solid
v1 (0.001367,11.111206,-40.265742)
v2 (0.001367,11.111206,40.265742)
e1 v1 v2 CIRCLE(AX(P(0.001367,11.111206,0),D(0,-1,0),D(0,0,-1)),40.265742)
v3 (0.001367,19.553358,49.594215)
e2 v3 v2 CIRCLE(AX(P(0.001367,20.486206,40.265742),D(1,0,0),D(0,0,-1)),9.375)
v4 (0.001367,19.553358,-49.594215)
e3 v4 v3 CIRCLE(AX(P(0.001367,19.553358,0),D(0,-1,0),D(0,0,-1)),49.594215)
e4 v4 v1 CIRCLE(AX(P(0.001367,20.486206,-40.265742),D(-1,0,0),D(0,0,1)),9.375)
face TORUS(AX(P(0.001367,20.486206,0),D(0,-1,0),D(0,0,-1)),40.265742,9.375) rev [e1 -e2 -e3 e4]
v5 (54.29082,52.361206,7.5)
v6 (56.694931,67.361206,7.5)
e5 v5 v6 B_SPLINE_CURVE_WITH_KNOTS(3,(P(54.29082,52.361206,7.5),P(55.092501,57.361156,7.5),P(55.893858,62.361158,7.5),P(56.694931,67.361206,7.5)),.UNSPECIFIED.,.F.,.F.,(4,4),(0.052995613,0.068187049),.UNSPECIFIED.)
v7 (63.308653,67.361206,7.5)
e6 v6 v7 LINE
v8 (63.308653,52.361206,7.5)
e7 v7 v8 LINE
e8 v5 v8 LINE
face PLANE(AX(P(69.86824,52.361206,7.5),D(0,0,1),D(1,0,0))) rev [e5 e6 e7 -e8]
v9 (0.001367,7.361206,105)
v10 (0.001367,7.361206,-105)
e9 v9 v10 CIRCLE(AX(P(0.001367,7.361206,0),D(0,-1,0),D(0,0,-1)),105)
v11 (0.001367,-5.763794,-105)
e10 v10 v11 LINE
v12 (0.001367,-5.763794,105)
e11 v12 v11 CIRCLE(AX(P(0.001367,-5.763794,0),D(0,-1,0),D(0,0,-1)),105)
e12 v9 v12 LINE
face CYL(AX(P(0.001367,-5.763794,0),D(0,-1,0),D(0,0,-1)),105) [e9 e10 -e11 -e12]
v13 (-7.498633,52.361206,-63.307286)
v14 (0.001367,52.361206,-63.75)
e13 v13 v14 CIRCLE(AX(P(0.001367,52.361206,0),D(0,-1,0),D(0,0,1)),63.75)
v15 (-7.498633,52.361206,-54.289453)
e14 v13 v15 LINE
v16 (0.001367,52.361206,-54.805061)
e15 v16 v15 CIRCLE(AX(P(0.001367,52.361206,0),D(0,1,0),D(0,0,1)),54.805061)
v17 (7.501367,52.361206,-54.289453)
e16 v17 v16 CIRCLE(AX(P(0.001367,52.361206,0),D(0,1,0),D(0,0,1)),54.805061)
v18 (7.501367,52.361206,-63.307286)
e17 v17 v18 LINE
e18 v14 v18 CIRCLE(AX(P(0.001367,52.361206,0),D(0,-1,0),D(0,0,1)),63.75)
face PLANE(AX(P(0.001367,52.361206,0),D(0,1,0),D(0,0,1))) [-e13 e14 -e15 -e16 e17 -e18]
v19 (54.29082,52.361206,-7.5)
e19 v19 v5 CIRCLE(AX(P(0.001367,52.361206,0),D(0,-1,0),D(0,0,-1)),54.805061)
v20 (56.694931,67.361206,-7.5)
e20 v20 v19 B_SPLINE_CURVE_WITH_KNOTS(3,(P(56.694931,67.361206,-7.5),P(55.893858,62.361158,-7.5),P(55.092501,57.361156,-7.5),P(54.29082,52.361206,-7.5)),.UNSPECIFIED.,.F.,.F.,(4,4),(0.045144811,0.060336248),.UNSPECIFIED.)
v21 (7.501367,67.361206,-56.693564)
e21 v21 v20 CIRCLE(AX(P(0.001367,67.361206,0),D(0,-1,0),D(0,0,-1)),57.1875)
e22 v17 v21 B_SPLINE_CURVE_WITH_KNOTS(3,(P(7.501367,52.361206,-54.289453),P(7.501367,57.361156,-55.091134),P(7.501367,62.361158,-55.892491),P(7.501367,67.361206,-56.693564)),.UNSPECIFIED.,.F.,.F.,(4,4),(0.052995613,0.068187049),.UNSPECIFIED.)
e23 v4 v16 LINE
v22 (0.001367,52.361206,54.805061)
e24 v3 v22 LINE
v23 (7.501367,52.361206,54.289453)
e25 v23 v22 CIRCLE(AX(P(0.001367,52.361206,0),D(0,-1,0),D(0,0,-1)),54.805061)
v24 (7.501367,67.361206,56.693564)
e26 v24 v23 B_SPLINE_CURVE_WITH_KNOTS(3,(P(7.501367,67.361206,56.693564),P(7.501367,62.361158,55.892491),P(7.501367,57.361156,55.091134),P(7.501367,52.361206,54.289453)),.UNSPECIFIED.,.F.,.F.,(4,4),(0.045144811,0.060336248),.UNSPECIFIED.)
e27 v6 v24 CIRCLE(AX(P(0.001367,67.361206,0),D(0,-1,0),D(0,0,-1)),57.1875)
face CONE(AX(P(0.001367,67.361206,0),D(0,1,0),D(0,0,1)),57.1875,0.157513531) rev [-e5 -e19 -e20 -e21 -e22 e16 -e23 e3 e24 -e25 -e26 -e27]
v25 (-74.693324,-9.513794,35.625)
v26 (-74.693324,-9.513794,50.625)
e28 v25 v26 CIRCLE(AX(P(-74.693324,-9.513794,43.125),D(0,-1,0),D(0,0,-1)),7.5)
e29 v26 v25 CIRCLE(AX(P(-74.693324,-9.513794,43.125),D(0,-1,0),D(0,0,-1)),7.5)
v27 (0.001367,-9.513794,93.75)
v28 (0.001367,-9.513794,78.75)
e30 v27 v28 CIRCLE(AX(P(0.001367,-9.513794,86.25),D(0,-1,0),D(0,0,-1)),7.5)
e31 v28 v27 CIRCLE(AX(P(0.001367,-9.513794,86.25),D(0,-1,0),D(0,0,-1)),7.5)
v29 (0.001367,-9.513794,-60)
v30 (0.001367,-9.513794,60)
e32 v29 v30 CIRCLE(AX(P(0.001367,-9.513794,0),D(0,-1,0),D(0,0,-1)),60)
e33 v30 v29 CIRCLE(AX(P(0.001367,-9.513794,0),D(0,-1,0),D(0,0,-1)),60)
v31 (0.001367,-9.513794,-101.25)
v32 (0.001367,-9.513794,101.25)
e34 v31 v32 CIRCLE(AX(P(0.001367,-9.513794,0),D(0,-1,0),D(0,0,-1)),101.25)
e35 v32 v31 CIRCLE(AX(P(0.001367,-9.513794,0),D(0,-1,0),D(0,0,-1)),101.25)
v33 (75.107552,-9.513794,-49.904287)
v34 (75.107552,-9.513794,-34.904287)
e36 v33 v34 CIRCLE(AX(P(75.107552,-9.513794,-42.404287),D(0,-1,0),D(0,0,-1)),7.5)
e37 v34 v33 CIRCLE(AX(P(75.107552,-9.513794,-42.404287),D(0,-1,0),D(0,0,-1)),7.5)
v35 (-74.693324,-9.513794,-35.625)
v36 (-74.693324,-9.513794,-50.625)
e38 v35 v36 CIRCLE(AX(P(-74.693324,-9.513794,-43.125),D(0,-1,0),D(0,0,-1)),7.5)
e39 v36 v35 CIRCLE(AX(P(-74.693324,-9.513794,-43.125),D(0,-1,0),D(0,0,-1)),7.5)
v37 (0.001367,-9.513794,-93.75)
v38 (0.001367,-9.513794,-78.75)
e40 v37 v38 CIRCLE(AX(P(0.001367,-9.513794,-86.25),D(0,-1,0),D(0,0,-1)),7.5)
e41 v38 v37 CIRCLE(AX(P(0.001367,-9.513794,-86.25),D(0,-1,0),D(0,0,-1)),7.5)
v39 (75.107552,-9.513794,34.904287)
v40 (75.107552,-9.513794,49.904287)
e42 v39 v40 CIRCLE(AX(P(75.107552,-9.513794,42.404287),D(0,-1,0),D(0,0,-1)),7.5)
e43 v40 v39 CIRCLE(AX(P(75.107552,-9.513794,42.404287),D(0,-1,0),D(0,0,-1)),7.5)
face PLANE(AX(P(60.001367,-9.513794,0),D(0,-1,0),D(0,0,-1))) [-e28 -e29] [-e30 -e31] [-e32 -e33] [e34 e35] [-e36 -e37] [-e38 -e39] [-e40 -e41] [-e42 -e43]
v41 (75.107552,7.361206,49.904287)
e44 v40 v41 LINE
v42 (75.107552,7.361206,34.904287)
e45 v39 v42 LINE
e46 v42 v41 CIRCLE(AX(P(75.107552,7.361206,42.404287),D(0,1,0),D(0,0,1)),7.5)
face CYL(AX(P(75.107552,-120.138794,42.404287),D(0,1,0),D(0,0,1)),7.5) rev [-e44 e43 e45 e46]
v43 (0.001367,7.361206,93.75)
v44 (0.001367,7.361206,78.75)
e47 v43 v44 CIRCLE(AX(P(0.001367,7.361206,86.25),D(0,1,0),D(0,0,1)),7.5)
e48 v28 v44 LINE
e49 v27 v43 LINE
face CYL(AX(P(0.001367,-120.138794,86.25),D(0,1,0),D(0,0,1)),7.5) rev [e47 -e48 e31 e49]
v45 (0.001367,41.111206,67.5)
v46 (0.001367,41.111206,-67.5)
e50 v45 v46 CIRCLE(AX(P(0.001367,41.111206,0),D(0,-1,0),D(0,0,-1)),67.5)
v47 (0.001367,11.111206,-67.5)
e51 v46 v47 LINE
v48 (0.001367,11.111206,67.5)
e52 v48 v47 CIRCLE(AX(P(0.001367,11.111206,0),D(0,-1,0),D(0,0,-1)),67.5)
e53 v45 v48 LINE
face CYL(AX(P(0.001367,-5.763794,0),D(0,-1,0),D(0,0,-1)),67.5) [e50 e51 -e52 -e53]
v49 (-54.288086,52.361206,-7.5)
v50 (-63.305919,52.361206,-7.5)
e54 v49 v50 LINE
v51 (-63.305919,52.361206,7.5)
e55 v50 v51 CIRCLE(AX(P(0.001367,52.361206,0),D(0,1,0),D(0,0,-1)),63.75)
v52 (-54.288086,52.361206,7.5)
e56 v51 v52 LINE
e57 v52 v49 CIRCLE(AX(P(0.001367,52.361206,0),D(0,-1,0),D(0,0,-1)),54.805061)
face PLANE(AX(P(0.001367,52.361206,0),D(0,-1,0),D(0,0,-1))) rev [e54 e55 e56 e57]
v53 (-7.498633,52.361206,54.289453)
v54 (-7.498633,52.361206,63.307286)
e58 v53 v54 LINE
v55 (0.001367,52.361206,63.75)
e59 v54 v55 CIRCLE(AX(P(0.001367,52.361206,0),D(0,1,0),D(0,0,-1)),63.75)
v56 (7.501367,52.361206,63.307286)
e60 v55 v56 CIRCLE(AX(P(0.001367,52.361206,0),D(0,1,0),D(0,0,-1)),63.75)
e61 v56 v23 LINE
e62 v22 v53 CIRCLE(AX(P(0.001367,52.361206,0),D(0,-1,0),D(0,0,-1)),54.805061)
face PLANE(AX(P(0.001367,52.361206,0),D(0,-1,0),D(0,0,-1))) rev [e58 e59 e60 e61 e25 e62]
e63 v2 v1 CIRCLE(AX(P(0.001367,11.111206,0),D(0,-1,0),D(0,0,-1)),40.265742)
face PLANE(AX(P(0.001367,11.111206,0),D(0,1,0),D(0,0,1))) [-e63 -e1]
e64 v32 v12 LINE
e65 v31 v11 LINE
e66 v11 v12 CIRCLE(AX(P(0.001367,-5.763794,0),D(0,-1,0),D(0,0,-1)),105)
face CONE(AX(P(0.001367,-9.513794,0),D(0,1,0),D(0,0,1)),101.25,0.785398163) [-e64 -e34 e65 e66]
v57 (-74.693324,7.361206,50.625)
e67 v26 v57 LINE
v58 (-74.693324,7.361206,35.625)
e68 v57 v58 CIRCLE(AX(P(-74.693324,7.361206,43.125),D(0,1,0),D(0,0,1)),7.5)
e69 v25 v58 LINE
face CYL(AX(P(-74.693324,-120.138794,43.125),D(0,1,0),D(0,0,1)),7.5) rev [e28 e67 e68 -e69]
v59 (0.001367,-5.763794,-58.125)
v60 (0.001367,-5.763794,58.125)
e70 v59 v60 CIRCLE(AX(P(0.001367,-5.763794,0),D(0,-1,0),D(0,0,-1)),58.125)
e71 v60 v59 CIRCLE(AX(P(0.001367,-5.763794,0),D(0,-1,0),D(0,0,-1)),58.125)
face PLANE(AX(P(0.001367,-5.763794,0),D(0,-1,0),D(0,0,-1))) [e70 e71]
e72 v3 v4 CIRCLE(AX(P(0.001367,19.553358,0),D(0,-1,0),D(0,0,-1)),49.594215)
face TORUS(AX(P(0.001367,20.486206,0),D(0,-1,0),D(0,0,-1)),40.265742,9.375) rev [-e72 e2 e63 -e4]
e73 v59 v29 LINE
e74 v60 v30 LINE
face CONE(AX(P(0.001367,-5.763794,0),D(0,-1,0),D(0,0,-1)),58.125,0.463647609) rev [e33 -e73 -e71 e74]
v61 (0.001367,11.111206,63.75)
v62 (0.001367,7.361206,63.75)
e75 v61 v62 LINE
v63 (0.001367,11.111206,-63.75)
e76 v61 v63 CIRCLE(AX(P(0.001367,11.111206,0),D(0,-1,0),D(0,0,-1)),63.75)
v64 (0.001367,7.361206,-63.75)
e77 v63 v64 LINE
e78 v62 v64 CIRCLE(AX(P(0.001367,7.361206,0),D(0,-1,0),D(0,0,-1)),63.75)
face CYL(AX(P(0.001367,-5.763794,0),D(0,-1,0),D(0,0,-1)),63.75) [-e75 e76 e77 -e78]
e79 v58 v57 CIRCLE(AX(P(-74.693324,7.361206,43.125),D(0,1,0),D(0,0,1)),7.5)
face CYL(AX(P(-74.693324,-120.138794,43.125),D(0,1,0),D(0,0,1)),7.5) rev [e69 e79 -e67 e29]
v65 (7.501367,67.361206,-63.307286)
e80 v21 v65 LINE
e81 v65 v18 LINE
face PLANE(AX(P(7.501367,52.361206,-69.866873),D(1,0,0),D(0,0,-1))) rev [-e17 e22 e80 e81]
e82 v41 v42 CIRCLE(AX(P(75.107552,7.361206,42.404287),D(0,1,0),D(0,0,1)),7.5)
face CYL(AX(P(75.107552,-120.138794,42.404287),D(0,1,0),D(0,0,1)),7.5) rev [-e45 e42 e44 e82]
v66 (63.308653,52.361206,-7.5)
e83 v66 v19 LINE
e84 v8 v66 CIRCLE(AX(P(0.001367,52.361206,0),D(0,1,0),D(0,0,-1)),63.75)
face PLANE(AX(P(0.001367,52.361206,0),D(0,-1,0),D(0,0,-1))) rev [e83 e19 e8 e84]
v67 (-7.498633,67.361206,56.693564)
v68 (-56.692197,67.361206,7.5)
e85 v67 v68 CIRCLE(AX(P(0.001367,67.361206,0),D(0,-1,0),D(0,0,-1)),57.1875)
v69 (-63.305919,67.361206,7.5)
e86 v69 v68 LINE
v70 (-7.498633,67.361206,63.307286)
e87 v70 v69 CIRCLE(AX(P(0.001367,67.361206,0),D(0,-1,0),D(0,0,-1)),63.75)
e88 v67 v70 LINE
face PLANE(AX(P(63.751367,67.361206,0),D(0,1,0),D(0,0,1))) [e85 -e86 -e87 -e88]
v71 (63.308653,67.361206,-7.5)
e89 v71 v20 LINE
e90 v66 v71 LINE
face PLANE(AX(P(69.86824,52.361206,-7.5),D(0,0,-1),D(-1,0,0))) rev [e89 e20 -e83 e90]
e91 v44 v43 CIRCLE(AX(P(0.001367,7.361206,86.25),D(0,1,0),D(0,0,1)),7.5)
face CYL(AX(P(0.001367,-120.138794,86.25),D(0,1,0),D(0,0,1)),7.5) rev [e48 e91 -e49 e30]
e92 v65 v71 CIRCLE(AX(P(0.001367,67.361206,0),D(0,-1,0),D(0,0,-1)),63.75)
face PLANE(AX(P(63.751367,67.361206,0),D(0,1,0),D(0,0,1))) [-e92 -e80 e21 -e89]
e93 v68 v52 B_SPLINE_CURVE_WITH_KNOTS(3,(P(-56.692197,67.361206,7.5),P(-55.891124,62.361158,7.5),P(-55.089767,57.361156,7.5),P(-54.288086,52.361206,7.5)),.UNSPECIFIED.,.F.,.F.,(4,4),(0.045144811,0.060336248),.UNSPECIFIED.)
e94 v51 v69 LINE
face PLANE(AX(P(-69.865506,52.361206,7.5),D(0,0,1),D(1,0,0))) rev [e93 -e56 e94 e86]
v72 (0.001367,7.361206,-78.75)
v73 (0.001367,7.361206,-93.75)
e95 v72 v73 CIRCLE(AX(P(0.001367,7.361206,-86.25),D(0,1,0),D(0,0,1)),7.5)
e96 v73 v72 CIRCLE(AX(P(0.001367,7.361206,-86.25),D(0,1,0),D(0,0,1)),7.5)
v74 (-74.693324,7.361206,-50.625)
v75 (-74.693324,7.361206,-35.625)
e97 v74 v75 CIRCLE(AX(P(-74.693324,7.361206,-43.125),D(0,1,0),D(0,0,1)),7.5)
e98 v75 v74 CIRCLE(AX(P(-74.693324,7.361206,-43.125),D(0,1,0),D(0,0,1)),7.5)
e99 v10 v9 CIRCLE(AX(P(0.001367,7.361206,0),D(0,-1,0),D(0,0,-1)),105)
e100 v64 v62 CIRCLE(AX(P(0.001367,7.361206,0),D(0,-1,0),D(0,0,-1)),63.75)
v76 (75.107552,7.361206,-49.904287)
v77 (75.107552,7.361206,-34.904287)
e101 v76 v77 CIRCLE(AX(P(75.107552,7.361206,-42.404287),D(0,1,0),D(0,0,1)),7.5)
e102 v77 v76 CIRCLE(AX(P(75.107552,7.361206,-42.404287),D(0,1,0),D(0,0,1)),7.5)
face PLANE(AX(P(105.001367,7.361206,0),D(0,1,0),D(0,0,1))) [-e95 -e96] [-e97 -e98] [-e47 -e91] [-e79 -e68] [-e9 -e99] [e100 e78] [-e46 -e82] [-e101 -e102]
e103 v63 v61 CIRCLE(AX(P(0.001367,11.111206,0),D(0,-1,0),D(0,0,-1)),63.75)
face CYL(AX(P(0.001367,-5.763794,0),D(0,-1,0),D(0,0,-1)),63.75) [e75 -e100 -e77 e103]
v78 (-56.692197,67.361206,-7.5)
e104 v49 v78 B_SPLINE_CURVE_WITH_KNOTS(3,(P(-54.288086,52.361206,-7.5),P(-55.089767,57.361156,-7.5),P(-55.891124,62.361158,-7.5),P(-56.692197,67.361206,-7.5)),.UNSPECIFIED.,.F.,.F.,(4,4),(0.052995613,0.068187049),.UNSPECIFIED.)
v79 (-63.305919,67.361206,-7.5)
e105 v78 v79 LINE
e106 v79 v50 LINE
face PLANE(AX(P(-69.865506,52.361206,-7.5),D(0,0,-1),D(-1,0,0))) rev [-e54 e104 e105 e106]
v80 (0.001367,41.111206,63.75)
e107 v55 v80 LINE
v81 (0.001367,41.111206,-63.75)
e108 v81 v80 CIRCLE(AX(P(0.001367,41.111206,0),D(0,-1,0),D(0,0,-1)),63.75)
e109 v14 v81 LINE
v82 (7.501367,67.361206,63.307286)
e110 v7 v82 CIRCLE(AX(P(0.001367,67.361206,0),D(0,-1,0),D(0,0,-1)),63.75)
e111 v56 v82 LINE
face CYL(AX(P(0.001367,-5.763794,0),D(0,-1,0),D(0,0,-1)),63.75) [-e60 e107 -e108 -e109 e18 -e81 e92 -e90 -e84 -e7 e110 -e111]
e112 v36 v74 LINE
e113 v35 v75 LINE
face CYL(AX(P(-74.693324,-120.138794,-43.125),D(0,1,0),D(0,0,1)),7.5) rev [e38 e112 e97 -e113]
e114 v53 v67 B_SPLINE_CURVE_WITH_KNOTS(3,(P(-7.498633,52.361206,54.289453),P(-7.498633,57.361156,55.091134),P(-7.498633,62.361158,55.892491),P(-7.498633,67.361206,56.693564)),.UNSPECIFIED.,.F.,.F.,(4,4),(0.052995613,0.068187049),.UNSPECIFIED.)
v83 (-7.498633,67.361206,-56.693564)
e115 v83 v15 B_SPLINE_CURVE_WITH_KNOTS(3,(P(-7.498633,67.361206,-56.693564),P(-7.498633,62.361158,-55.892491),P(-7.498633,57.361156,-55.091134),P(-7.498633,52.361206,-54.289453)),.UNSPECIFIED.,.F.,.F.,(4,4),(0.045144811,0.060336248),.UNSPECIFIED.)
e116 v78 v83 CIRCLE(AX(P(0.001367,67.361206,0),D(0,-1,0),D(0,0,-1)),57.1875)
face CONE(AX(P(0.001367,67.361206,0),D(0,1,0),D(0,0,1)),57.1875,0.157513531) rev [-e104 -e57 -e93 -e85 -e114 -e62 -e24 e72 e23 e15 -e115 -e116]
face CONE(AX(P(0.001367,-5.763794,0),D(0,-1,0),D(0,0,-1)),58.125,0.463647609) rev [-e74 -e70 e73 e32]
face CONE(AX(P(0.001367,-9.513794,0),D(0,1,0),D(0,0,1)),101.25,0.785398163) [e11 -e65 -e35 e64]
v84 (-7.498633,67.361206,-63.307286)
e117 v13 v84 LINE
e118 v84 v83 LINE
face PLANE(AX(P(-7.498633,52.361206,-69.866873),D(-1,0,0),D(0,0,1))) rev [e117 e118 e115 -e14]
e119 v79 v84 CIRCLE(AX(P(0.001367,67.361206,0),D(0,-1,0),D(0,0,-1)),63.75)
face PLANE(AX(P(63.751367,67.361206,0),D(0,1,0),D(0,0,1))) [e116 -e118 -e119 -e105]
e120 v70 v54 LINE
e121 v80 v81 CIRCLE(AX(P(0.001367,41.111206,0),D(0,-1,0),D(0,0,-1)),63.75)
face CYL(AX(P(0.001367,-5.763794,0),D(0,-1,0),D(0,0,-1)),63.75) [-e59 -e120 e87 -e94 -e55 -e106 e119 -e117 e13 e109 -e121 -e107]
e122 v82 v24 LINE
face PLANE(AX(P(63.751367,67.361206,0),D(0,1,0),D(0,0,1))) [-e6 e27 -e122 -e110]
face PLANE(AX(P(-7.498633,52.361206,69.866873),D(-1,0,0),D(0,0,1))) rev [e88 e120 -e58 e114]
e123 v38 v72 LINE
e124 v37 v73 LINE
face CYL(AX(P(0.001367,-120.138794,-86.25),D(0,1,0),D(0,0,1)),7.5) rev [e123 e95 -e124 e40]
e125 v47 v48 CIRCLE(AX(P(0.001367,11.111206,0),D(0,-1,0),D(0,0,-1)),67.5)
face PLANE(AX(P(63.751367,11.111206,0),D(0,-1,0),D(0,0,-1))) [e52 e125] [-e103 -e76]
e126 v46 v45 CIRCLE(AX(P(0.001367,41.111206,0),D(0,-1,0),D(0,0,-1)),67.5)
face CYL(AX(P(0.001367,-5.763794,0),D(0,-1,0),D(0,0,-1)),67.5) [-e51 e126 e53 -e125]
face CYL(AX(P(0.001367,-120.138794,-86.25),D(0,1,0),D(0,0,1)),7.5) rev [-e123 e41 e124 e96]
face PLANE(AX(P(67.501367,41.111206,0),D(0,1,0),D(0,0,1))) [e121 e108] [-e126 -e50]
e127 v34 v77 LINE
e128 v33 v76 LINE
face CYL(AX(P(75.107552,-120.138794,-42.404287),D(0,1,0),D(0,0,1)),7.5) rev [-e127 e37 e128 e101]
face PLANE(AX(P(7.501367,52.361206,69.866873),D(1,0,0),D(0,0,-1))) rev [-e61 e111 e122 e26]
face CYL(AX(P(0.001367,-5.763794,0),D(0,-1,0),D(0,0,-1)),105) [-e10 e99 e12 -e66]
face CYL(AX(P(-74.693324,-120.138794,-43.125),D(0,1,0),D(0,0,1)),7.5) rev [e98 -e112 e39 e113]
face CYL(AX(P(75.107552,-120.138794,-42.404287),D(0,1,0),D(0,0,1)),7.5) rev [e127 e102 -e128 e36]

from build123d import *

# Parameters (mm, degrees)
SKETCH2_W          = 20
SKETCH2_H          = 8
SKETCH2_W_2        = 8
SKETCH2_H_2        = 20
CUT_EXTRUDE1_DEPTH = 8
SKETCH3_R          = 4
CUT_EXTRUDE2_DEPTH = 100
SCALE_1_SCALE      = 1.875


with BuildPart() as part:
    # Sketch1 → Revolve1 (revolve)
    with BuildSketch(Plane.XY, mode=Mode.PRIVATE) as revolve1_sk:
        with BuildLine():
            Line((32, 0), (54, 0))
            Line((54, 0), (56, 2))
            Line((56, 2), (56, 9))
            Line((56, 9), (36, 9))
            Line((36, 9), (34, 9))
            Line((34, 9), (34, 11))
            Line((34, 11), (36, 11))
            Line((36, 11), (36, 27))
            Line((36, 27), (34, 27))
            Line((34, 27), (34, 41))
            Line((34, 41), (30.5, 41))
            Line((30.5, 41), (26.45024814, 15.502481405))
            ThreePointArc((26.45024814, 15.502481405), (24.830088793, 12.292737332), (21.475062189, 11))
            Line((21.475062189, 11), (0, 11))
            Line((0, 11), (0, 2))
            Line((0, 2), (31, 2))
            Line((31, 2), (32, 0))
        make_face()
    revolve(revolve1_sk.sketch.rotate(Axis((0, 2, 0), (0, 1, 0)), 90), axis=Axis((0, 2, 0), (0, 1, 0)))

    # Sketch2 → Cut-Extrude1 (cut)
    with BuildSketch(Plane(origin=(0, 41, 0), x_dir=(1, 0, 0), z_dir=(0, 1, 0))):
        with Locations((27.262332301, 0)):
            Rectangle(SKETCH2_W, SKETCH2_H)
        with Locations((0, 27.262332301)):
            Rectangle(SKETCH2_W_2, SKETCH2_H_2)
        with Locations((0, -27.262332301)):
            Rectangle(SKETCH2_W_2, SKETCH2_H_2)
        with Locations((-27.262332301, 0)):
            Rectangle(SKETCH2_W, SKETCH2_H)
    extrude(amount=-CUT_EXTRUDE1_DEPTH, mode=Mode.SUBTRACT)

    # Sketch3 → Cut-Extrude2 (cut)
    with BuildSketch(Plane(origin=(0, 41, 0), x_dir=(1, 0, 0), z_dir=(0, 1, 0))):
        with Locations(Location((0, 46, 0), (0, 0, 270))):
            Circle(SKETCH3_R)
        with Locations(Location((40.056631801, 22.615619575, 0), (0, 0, 270))):
            Circle(SKETCH3_R)
        with Locations(Location((-39.837168574, 23, 0), (0, 0, 270))):
            Circle(SKETCH3_R)
        with Locations(Location((-39.837168574, -23, 0), (0, 0, 270))):
            Circle(SKETCH3_R)
        with Locations(Location((0, -46, 0), (0, 0, 270))):
            Circle(SKETCH3_R)
        with Locations(Location((40.056631801, -22.615619575, 0), (0, 0, 270))):
            Circle(SKETCH3_R)
    extrude(amount=-CUT_EXTRUDE2_DEPTH, mode=Mode.SUBTRACT)


with BuildPart() as part_1:
    # Scale 1: scaled about (-0.001562363, 10.8729077, 0)
    add(part.part.scale(SCALE_1_SCALE).moved(Location((0.001367068, -9.513794238, 0))))


solid = part_1.part
